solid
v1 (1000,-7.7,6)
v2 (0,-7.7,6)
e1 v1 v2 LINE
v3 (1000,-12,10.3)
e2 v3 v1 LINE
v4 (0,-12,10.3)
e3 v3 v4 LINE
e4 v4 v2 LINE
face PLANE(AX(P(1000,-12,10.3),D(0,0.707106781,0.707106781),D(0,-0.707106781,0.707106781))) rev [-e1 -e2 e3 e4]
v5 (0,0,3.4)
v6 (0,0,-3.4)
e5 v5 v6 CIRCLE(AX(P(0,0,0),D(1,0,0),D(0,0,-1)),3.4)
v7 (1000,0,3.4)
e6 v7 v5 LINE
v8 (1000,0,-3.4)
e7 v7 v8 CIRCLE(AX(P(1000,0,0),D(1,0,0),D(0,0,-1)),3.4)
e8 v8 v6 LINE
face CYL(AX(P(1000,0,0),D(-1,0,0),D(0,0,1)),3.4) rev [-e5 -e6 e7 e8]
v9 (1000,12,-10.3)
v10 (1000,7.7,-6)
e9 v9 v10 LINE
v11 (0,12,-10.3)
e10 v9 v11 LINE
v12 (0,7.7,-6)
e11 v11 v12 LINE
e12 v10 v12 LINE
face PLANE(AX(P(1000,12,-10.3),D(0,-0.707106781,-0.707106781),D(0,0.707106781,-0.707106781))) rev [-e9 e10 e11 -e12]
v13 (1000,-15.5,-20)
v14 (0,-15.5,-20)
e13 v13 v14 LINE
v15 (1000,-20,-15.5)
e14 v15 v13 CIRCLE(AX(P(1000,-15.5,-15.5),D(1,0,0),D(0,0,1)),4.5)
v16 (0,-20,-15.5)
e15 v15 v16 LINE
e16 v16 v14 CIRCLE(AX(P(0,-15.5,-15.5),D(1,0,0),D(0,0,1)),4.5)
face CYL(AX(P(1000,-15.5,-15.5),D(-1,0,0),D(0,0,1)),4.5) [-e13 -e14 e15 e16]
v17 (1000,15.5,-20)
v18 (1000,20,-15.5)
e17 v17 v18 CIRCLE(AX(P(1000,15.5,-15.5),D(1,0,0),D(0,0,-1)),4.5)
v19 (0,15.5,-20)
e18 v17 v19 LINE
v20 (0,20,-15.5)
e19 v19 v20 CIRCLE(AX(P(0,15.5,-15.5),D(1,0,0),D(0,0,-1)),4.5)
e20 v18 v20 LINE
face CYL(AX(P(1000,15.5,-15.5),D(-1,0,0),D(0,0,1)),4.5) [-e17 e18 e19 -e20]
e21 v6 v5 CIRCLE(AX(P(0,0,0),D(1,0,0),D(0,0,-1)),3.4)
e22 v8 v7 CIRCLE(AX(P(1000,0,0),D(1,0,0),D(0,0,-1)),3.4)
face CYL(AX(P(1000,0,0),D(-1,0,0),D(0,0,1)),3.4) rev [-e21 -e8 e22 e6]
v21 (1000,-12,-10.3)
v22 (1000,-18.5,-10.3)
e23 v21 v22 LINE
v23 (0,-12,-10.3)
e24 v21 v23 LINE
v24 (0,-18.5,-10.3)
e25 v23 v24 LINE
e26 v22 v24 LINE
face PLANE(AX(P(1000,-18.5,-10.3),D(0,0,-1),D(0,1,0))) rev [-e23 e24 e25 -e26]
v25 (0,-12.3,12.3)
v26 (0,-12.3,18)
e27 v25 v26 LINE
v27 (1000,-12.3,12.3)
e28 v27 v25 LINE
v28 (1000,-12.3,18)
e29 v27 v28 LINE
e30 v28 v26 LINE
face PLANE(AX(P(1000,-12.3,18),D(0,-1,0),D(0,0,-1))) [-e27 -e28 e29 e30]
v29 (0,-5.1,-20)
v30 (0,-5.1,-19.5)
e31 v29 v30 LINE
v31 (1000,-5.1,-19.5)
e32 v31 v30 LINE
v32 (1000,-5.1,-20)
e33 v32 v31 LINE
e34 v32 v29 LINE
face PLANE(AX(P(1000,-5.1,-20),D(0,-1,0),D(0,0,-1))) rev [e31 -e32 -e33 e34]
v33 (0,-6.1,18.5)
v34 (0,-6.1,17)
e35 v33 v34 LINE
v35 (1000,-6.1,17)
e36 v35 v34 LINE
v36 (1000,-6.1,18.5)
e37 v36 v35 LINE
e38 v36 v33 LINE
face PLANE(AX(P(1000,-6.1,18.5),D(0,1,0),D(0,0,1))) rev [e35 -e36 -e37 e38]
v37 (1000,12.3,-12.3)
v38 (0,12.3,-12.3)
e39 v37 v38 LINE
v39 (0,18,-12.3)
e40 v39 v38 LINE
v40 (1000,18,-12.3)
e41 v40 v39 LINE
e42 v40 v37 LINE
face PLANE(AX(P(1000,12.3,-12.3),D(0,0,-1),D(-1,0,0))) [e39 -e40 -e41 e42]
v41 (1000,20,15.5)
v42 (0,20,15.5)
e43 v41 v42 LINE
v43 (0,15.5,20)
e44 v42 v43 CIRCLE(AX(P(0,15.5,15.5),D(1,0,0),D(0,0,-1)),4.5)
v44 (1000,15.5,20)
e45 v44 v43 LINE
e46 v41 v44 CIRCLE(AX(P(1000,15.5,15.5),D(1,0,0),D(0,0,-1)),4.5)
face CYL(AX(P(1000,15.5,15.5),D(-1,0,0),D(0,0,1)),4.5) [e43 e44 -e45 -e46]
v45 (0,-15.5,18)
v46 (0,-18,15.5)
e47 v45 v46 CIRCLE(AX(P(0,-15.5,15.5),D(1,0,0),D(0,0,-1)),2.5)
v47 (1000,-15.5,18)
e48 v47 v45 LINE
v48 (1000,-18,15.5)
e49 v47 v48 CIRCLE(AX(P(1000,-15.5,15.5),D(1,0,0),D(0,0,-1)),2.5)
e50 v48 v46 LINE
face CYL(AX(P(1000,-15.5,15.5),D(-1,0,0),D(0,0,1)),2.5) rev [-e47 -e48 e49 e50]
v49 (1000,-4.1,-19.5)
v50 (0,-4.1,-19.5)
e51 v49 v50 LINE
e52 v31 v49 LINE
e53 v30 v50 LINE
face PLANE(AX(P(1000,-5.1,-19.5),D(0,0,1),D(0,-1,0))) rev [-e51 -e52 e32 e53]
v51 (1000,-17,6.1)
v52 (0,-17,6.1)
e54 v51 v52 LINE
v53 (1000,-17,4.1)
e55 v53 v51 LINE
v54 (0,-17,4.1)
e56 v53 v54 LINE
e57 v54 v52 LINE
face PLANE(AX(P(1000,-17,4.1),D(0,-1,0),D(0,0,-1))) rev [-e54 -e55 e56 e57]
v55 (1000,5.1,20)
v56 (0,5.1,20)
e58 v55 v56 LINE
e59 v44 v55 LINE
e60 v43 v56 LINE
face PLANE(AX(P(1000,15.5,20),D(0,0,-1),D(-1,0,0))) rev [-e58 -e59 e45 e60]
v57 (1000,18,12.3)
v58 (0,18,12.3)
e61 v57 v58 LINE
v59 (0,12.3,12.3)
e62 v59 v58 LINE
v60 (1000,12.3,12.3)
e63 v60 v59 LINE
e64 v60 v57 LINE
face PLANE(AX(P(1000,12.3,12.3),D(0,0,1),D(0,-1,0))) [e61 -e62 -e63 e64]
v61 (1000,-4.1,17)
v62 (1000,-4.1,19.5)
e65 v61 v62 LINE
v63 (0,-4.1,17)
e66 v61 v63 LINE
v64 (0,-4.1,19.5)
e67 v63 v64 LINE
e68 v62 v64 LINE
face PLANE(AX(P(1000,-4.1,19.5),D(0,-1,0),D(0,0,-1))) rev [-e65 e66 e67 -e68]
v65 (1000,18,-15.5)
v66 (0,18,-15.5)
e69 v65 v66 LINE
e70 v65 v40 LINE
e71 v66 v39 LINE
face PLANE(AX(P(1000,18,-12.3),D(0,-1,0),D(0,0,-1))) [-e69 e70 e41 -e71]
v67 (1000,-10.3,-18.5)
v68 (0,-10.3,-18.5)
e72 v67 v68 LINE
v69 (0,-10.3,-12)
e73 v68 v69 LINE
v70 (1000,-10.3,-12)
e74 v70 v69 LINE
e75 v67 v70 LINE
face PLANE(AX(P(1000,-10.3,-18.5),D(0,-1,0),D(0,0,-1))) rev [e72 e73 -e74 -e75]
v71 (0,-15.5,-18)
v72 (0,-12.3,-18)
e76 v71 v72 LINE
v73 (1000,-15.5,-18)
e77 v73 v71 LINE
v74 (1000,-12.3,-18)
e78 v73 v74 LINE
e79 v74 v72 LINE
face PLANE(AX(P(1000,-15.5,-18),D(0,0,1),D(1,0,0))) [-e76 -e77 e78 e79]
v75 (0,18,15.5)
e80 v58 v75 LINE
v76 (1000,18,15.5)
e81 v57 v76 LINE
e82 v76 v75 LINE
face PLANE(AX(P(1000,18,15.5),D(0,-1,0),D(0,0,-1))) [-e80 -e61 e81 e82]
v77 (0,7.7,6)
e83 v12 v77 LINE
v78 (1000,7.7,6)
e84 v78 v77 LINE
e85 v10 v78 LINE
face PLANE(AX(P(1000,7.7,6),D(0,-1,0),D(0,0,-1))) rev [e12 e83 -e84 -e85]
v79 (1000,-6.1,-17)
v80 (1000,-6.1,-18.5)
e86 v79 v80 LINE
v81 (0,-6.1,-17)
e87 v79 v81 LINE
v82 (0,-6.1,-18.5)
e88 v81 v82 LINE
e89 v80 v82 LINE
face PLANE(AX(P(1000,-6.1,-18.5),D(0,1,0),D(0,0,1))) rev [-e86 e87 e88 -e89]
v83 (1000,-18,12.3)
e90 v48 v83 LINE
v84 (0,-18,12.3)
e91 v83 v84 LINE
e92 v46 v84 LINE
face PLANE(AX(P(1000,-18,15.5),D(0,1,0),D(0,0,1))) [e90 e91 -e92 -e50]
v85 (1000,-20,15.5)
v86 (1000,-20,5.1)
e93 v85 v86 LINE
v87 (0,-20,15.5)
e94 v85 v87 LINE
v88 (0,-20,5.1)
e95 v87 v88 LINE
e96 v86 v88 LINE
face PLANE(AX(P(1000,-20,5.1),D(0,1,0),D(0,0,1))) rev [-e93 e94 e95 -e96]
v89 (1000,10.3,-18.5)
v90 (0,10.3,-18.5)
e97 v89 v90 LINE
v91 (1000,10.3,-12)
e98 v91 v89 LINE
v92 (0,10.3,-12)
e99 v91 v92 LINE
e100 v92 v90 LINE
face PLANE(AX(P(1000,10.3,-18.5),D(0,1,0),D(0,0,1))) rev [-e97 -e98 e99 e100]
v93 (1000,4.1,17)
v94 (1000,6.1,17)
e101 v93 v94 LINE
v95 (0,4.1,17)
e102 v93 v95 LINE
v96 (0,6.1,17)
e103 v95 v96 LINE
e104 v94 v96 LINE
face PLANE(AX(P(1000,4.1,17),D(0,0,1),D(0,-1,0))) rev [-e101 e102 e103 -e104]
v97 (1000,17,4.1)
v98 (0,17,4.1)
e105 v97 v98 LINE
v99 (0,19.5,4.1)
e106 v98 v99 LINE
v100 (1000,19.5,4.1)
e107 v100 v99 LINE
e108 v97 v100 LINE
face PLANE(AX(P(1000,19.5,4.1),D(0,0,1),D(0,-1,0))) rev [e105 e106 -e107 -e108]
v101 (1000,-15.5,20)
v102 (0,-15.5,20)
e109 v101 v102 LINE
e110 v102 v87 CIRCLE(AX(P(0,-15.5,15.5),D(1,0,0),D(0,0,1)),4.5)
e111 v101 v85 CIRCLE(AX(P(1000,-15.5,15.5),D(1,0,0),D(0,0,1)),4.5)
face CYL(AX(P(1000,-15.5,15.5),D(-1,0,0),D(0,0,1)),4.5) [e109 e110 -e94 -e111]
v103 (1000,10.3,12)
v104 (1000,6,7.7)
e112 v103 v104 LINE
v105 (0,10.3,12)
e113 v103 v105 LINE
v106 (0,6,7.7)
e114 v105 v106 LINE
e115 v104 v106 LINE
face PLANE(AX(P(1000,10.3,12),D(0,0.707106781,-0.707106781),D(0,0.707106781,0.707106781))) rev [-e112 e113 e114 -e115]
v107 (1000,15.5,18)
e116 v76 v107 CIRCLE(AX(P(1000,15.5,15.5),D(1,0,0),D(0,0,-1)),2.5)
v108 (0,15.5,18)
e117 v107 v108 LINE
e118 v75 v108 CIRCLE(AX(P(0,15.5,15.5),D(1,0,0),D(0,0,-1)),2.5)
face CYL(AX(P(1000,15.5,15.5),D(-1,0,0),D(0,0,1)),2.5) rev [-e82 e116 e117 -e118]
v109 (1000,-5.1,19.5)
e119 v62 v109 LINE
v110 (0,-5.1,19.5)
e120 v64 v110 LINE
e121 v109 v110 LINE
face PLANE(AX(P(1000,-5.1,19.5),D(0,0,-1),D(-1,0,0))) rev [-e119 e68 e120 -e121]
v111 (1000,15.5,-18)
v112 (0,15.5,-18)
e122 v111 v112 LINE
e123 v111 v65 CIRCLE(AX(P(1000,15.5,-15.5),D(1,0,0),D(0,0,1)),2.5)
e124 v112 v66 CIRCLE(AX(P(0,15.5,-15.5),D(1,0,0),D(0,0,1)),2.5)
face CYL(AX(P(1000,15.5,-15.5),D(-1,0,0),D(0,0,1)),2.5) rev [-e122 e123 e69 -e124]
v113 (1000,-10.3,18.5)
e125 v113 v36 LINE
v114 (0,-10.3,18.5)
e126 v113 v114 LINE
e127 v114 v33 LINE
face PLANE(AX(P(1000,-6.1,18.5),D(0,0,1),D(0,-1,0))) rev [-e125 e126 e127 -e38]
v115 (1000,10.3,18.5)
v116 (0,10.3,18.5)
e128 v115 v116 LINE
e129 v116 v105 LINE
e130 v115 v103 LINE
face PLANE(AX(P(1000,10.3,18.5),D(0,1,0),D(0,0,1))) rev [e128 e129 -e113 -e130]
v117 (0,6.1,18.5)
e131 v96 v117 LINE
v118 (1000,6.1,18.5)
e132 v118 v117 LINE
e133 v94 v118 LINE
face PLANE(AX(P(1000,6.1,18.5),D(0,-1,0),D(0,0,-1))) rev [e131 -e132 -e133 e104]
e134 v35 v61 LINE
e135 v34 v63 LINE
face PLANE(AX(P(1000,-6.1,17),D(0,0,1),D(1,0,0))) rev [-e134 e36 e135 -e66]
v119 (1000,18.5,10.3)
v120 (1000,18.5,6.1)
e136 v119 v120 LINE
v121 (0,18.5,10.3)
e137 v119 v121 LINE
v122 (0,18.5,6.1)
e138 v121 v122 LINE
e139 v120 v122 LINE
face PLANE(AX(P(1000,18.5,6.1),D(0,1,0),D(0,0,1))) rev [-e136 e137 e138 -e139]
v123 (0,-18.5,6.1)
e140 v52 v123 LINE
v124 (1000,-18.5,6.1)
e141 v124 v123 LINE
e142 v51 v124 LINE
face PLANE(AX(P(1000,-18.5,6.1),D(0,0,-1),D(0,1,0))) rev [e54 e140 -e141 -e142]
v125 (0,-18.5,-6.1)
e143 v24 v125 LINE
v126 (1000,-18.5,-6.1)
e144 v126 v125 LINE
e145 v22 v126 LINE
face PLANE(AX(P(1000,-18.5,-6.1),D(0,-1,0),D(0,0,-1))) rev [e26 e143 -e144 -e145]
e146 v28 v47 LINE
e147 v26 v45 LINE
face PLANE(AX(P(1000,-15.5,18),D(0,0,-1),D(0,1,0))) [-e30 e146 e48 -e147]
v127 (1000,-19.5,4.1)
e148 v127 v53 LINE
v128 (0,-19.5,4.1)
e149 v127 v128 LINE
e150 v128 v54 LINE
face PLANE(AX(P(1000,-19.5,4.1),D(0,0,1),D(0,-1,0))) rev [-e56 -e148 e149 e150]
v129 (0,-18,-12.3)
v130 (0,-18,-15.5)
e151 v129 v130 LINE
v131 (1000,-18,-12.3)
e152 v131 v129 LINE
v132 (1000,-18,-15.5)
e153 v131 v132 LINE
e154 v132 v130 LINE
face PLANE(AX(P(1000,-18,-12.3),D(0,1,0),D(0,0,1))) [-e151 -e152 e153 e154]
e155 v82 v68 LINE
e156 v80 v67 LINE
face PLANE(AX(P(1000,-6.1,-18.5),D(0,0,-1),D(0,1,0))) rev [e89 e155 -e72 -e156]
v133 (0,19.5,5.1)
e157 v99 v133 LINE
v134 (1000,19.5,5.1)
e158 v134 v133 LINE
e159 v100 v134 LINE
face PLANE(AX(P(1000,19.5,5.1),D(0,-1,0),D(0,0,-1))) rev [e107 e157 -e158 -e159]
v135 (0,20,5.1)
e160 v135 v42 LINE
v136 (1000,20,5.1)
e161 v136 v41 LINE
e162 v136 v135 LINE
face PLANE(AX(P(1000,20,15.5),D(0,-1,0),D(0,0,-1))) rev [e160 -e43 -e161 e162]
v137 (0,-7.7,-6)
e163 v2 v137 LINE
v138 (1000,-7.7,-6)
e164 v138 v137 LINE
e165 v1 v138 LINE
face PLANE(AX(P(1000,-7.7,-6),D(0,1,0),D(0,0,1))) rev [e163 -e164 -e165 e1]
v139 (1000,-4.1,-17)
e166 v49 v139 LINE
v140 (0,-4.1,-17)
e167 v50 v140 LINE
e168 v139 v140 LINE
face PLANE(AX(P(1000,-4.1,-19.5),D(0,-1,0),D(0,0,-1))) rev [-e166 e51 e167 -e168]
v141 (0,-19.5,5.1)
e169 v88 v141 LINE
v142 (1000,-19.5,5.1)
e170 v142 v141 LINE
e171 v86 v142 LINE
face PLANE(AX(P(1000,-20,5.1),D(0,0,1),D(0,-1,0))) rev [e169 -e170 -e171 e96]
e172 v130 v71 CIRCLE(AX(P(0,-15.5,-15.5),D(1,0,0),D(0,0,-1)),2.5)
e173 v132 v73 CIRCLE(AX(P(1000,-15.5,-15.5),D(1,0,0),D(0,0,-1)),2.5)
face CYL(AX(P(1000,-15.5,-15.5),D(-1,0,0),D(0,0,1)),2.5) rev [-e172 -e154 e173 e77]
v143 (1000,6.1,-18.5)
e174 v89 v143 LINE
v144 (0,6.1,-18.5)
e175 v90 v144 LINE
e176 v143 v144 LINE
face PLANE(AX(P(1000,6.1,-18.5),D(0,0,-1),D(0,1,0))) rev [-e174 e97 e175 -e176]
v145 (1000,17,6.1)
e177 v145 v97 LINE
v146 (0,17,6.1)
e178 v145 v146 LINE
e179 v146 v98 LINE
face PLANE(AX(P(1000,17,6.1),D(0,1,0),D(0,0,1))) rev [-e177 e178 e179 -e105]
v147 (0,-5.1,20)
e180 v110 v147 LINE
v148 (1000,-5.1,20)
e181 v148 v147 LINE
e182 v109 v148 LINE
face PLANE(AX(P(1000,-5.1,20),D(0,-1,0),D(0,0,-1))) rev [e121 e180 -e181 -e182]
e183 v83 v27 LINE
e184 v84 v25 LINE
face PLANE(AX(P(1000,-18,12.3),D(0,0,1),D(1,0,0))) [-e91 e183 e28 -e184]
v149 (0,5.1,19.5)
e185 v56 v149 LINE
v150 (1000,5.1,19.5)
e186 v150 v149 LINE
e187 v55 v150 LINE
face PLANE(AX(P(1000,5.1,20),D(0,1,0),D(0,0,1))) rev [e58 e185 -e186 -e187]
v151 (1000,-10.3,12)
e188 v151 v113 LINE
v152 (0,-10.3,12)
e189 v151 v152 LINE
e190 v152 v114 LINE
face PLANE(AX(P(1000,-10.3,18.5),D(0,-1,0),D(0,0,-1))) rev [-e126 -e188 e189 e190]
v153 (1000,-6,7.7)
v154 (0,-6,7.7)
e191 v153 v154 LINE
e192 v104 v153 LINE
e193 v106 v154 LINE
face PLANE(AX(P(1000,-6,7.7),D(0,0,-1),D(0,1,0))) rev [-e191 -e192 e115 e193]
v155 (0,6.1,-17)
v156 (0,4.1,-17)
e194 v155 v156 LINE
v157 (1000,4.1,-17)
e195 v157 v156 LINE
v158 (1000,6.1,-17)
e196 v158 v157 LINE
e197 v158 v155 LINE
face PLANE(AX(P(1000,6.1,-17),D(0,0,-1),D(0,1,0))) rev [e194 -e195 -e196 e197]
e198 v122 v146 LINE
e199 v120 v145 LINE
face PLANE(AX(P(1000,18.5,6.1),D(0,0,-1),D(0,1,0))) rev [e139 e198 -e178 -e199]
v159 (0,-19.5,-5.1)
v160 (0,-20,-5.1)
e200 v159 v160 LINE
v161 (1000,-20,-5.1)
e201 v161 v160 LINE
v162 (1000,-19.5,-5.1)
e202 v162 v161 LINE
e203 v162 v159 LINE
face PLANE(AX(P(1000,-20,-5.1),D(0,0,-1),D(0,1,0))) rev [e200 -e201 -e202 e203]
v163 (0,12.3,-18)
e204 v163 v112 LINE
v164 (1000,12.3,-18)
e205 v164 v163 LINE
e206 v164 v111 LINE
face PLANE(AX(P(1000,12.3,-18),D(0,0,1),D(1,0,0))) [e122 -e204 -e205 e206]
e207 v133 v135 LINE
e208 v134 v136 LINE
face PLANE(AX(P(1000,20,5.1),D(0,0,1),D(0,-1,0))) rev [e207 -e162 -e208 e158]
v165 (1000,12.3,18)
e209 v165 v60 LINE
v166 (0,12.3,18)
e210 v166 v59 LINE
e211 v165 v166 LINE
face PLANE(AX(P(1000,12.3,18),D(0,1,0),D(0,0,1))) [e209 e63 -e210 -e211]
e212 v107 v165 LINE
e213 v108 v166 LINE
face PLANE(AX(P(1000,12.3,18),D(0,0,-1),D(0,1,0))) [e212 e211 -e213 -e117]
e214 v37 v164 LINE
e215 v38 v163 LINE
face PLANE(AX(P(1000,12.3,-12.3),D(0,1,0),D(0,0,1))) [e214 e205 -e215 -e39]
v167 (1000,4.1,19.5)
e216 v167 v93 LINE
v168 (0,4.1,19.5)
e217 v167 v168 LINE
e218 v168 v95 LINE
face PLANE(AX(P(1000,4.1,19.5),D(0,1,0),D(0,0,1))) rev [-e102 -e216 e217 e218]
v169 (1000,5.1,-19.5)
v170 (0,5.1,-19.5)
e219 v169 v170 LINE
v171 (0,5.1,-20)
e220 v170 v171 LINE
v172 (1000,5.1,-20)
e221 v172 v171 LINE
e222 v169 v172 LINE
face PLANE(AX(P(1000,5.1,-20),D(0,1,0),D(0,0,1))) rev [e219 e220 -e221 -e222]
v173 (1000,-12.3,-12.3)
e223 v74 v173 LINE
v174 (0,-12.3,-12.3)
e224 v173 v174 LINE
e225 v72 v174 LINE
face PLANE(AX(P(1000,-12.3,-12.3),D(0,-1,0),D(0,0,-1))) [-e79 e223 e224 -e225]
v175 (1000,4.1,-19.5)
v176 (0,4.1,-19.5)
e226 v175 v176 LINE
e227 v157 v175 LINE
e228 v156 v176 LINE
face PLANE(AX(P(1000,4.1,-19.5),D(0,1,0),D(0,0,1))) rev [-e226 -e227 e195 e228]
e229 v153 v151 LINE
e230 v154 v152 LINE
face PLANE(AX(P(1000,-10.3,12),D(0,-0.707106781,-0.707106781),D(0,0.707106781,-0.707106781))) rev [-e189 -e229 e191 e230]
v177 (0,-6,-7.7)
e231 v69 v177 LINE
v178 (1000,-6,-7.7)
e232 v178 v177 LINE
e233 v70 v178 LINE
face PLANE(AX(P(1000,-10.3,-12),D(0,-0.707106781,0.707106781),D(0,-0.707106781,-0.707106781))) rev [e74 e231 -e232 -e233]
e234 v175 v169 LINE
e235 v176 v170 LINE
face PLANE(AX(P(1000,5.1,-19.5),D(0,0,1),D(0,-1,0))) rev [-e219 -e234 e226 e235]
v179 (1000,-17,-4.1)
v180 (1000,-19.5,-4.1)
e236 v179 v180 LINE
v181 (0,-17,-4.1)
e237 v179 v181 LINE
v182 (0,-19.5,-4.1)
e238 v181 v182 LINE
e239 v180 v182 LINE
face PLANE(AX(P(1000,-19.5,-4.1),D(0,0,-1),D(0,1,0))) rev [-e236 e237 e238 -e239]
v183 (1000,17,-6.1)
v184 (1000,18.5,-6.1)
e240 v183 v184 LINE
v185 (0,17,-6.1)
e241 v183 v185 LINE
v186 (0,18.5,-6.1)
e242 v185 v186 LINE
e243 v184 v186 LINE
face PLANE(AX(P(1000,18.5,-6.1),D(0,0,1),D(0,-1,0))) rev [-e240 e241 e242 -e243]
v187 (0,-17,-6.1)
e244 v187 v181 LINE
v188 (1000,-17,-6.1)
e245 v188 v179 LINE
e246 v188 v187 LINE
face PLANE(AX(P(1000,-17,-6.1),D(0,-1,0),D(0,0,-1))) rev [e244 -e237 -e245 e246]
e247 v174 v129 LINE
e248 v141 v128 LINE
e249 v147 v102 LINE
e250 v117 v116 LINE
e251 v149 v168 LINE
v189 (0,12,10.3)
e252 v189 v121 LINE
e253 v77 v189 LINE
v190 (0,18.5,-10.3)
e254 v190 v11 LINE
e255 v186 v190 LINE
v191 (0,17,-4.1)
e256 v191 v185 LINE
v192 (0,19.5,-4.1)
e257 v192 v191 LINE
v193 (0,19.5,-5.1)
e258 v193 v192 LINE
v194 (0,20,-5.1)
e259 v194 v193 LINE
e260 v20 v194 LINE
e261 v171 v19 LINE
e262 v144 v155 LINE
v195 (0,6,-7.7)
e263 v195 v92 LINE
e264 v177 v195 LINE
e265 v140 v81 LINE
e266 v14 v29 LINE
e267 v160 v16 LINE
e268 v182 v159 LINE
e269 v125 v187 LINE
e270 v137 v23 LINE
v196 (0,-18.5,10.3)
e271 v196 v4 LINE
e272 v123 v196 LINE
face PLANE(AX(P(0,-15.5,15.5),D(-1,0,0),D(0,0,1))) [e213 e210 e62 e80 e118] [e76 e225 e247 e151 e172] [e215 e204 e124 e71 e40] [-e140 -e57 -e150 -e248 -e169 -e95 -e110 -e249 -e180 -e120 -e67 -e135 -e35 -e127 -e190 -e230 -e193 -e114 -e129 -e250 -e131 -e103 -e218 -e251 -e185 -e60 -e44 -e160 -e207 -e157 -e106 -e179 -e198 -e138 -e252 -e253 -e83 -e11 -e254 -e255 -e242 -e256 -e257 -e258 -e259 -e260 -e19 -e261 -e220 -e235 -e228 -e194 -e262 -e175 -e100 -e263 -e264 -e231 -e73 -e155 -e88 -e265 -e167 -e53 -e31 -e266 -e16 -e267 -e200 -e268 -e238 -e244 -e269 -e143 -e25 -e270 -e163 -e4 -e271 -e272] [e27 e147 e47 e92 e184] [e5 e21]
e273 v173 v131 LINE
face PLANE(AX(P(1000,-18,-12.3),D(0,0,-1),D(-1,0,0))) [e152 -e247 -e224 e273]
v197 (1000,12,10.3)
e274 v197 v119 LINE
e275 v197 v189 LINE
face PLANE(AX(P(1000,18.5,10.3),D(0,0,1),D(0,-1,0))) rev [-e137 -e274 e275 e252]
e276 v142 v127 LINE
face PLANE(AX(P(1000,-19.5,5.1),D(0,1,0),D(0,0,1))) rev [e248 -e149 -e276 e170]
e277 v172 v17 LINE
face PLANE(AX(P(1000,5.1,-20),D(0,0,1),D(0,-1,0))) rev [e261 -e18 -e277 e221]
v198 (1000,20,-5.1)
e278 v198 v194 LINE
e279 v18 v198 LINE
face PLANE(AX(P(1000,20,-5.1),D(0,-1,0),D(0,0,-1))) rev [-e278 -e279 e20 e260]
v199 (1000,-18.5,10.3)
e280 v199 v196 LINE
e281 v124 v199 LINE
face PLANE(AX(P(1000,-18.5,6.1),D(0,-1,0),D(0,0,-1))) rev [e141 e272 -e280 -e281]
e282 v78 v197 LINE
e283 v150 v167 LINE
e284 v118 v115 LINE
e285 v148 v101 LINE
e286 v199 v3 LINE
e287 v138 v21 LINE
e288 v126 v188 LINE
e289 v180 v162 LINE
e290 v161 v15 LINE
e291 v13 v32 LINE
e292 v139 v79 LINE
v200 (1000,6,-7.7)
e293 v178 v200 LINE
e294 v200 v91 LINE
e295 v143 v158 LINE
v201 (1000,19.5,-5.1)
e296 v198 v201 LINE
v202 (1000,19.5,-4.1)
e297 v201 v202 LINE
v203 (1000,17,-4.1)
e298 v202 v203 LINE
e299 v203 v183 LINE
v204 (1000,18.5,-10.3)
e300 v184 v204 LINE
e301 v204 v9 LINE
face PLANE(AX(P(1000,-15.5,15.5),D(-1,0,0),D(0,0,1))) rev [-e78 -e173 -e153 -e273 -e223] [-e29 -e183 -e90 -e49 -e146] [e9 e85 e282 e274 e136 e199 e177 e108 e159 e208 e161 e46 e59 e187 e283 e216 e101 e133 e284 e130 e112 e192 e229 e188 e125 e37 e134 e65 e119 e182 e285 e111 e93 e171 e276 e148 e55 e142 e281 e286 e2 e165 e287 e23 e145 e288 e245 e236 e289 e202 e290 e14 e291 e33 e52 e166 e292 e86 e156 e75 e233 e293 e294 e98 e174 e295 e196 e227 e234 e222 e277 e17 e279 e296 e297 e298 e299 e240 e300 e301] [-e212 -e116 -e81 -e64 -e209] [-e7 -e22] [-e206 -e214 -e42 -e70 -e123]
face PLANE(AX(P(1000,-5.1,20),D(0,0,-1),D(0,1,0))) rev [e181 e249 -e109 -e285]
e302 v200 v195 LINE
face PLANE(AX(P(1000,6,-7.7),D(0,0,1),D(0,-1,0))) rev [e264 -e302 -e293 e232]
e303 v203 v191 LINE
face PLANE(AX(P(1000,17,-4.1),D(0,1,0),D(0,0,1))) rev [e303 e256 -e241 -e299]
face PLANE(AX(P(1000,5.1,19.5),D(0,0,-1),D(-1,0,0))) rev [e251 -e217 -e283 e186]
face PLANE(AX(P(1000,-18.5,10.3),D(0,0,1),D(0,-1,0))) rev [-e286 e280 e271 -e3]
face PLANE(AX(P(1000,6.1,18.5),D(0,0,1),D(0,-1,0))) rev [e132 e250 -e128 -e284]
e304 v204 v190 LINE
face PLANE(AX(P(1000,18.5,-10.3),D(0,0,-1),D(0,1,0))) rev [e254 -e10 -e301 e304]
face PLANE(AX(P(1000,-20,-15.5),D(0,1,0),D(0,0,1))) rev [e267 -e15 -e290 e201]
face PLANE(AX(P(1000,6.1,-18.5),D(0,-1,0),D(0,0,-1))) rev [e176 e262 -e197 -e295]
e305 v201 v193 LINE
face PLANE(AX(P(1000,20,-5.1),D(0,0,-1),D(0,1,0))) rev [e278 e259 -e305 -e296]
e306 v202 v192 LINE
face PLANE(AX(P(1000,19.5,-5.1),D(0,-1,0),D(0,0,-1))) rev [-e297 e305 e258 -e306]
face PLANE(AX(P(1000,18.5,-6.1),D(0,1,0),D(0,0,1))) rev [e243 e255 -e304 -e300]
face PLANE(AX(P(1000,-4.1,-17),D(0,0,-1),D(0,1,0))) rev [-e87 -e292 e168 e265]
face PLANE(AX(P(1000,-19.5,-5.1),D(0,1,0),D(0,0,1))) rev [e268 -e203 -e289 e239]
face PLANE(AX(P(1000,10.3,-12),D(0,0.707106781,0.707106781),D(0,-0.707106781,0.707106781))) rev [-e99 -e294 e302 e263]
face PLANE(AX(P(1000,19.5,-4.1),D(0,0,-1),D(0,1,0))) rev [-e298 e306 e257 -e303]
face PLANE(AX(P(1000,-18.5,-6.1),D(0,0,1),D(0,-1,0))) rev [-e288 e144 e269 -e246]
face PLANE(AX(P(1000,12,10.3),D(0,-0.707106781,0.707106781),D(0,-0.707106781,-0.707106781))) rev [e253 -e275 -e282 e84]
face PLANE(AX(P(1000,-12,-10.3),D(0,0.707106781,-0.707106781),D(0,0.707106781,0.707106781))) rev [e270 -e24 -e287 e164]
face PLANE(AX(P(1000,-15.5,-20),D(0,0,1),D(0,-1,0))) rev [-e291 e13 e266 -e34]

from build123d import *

# Parameters (mm, degrees)
SKETCH1_R                                = 3.4
ALUMINUM_PROFILE_40_X_40B_X_R4_5_1_DEPTH = 1000


with BuildPart() as part:
    # Sketch1 → Aluminum profile 40 X 40B X R4.5(1) (new body)
    with BuildSketch(Plane.YZ):
        with BuildLine():
            Line((-5.1, 20), (-5.1, 19.5))
            Line((-5.1, 19.5), (-4.1, 19.5))
            Line((-4.1, 19.5), (-4.1, 17))
            Line((-4.1, 17), (-6.1, 17))
            Line((-6.1, 17), (-6.1, 18.5))
            Line((-6.1, 18.5), (-10.3, 18.5))
            Line((-10.3, 18.5), (-10.3, 12))
            Line((-10.3, 12), (-6, 7.7))
            Line((-6, 7.7), (6, 7.7))
            Line((6, 7.7), (10.3, 12))
            Line((10.3, 12), (10.3, 18.5))
            Line((10.3, 18.5), (6.1, 18.5))
            Line((6.1, 18.5), (6.1, 17))
            Line((6.1, 17), (4.1, 17))
            Line((4.1, 17), (4.1, 19.5))
            Line((4.1, 19.5), (5.1, 19.5))
            Line((5.1, 19.5), (5.1, 20))
            Line((5.1, 20), (15.5, 20))
            ThreePointArc((15.5, 20), (18.681980515, 18.681980515), (20, 15.5))
            Line((20, 15.5), (20, 5.1))
            Line((20, 5.1), (19.5, 5.1))
            Line((19.5, 5.1), (19.5, 4.1))
            Line((19.5, 4.1), (17, 4.1))
            Line((17, 4.1), (17, 6.1))
            Line((17, 6.1), (18.5, 6.1))
            Line((18.5, 6.1), (18.5, 10.3))
            Line((18.5, 10.3), (12, 10.3))
            Line((12, 10.3), (7.7, 6))
            Line((7.7, 6), (7.7, -6))
            Line((7.7, -6), (12, -10.3))
            Line((12, -10.3), (18.5, -10.3))
            Line((18.5, -10.3), (18.5, -6.1))
            Line((18.5, -6.1), (17, -6.1))
            Line((17, -6.1), (17, -4.1))
            Line((17, -4.1), (19.5, -4.1))
            Line((19.5, -4.1), (19.5, -5.1))
            Line((19.5, -5.1), (20, -5.1))
            Line((20, -5.1), (20, -15.5))
            ThreePointArc((20, -15.5), (18.681980515, -18.681980515), (15.5, -20))
            Line((15.5, -20), (5.1, -20))
            Line((5.1, -20), (5.1, -19.5))
            Line((5.1, -19.5), (4.1, -19.5))
            Line((4.1, -19.5), (4.1, -17))
            Line((4.1, -17), (6.1, -17))
            Line((6.1, -17), (6.1, -18.5))
            Line((6.1, -18.5), (10.3, -18.5))
            Line((10.3, -18.5), (10.3, -12))
            Line((10.3, -12), (6, -7.7))
            Line((6, -7.7), (-6, -7.7))
            Line((-6, -7.7), (-10.3, -12))
            Line((-10.3, -12), (-10.3, -18.5))
            Line((-10.3, -18.5), (-6.1, -18.5))
            Line((-6.1, -18.5), (-6.1, -17))
            Line((-6.1, -17), (-4.1, -17))
            Line((-4.1, -17), (-4.1, -19.5))
            Line((-4.1, -19.5), (-5.1, -19.5))
            Line((-5.1, -19.5), (-5.1, -20))
            Line((-5.1, -20), (-15.5, -20))
            ThreePointArc((-15.5, -20), (-18.681980515, -18.681980515), (-20, -15.5))
            Line((-20, -15.5), (-20, -5.1))
            Line((-20, -5.1), (-19.5, -5.1))
            Line((-19.5, -5.1), (-19.5, -4.1))
            Line((-19.5, -4.1), (-17, -4.1))
            Line((-17, -4.1), (-17, -6.1))
            Line((-17, -6.1), (-18.5, -6.1))
            Line((-18.5, -6.1), (-18.5, -10.3))
            Line((-18.5, -10.3), (-12, -10.3))
            Line((-12, -10.3), (-7.7, -6))
            Line((-7.7, -6), (-7.7, 6))
            Line((-7.7, 6), (-12, 10.3))
            Line((-12, 10.3), (-18.5, 10.3))
            Line((-18.5, 10.3), (-18.5, 6.1))
            Line((-18.5, 6.1), (-17, 6.1))
            Line((-17, 6.1), (-17, 4.1))
            Line((-17, 4.1), (-19.5, 4.1))
            Line((-19.5, 4.1), (-19.5, 5.1))
            Line((-19.5, 5.1), (-20, 5.1))
            Line((-20, 5.1), (-20, 15.5))
            ThreePointArc((-20, 15.5), (-18.681980515, 18.681980515), (-15.5, 20))
            Line((-15.5, 20), (-5.1, 20))
        make_face()
        Circle(SKETCH1_R, mode=Mode.SUBTRACT)
        with BuildLine():
            Line((12.3, 18), (15.5, 18))
            ThreePointArc((15.5, 18), (17.267766953, 17.267766953), (18, 15.5))
            Line((18, 15.5), (18, 12.3))
            Line((18, 12.3), (12.3, 12.3))
            Line((12.3, 12.3), (12.3, 18))
        make_face(mode=Mode.SUBTRACT)
        with BuildLine():
            Line((-15.5, 18), (-12.3, 18))
            Line((-12.3, 18), (-12.3, 12.3))
            Line((-12.3, 12.3), (-18, 12.3))
            Line((-18, 12.3), (-18, 15.5))
            ThreePointArc((-18, 15.5), (-17.267766953, 17.267766953), (-15.5, 18))
        make_face(mode=Mode.SUBTRACT)
        with BuildLine():
            Line((-18, -12.3), (-12.3, -12.3))
            Line((-12.3, -12.3), (-12.3, -18))
            Line((-12.3, -18), (-15.5, -18))
            ThreePointArc((-15.5, -18), (-17.267766953, -17.267766953), (-18, -15.5))
            Line((-18, -15.5), (-18, -12.3))
        make_face(mode=Mode.SUBTRACT)
        with BuildLine():
            Line((12.3, -12.3), (18, -12.3))
            Line((18, -12.3), (18, -15.5))
            ThreePointArc((18, -15.5), (17.267766953, -17.267766953), (15.5, -18))
            Line((15.5, -18), (12.3, -18))
            Line((12.3, -18), (12.3, -12.3))
        make_face(mode=Mode.SUBTRACT)
    extrude(amount=ALUMINUM_PROFILE_40_X_40B_X_R4_5_1_DEPTH)


solid = part.part
